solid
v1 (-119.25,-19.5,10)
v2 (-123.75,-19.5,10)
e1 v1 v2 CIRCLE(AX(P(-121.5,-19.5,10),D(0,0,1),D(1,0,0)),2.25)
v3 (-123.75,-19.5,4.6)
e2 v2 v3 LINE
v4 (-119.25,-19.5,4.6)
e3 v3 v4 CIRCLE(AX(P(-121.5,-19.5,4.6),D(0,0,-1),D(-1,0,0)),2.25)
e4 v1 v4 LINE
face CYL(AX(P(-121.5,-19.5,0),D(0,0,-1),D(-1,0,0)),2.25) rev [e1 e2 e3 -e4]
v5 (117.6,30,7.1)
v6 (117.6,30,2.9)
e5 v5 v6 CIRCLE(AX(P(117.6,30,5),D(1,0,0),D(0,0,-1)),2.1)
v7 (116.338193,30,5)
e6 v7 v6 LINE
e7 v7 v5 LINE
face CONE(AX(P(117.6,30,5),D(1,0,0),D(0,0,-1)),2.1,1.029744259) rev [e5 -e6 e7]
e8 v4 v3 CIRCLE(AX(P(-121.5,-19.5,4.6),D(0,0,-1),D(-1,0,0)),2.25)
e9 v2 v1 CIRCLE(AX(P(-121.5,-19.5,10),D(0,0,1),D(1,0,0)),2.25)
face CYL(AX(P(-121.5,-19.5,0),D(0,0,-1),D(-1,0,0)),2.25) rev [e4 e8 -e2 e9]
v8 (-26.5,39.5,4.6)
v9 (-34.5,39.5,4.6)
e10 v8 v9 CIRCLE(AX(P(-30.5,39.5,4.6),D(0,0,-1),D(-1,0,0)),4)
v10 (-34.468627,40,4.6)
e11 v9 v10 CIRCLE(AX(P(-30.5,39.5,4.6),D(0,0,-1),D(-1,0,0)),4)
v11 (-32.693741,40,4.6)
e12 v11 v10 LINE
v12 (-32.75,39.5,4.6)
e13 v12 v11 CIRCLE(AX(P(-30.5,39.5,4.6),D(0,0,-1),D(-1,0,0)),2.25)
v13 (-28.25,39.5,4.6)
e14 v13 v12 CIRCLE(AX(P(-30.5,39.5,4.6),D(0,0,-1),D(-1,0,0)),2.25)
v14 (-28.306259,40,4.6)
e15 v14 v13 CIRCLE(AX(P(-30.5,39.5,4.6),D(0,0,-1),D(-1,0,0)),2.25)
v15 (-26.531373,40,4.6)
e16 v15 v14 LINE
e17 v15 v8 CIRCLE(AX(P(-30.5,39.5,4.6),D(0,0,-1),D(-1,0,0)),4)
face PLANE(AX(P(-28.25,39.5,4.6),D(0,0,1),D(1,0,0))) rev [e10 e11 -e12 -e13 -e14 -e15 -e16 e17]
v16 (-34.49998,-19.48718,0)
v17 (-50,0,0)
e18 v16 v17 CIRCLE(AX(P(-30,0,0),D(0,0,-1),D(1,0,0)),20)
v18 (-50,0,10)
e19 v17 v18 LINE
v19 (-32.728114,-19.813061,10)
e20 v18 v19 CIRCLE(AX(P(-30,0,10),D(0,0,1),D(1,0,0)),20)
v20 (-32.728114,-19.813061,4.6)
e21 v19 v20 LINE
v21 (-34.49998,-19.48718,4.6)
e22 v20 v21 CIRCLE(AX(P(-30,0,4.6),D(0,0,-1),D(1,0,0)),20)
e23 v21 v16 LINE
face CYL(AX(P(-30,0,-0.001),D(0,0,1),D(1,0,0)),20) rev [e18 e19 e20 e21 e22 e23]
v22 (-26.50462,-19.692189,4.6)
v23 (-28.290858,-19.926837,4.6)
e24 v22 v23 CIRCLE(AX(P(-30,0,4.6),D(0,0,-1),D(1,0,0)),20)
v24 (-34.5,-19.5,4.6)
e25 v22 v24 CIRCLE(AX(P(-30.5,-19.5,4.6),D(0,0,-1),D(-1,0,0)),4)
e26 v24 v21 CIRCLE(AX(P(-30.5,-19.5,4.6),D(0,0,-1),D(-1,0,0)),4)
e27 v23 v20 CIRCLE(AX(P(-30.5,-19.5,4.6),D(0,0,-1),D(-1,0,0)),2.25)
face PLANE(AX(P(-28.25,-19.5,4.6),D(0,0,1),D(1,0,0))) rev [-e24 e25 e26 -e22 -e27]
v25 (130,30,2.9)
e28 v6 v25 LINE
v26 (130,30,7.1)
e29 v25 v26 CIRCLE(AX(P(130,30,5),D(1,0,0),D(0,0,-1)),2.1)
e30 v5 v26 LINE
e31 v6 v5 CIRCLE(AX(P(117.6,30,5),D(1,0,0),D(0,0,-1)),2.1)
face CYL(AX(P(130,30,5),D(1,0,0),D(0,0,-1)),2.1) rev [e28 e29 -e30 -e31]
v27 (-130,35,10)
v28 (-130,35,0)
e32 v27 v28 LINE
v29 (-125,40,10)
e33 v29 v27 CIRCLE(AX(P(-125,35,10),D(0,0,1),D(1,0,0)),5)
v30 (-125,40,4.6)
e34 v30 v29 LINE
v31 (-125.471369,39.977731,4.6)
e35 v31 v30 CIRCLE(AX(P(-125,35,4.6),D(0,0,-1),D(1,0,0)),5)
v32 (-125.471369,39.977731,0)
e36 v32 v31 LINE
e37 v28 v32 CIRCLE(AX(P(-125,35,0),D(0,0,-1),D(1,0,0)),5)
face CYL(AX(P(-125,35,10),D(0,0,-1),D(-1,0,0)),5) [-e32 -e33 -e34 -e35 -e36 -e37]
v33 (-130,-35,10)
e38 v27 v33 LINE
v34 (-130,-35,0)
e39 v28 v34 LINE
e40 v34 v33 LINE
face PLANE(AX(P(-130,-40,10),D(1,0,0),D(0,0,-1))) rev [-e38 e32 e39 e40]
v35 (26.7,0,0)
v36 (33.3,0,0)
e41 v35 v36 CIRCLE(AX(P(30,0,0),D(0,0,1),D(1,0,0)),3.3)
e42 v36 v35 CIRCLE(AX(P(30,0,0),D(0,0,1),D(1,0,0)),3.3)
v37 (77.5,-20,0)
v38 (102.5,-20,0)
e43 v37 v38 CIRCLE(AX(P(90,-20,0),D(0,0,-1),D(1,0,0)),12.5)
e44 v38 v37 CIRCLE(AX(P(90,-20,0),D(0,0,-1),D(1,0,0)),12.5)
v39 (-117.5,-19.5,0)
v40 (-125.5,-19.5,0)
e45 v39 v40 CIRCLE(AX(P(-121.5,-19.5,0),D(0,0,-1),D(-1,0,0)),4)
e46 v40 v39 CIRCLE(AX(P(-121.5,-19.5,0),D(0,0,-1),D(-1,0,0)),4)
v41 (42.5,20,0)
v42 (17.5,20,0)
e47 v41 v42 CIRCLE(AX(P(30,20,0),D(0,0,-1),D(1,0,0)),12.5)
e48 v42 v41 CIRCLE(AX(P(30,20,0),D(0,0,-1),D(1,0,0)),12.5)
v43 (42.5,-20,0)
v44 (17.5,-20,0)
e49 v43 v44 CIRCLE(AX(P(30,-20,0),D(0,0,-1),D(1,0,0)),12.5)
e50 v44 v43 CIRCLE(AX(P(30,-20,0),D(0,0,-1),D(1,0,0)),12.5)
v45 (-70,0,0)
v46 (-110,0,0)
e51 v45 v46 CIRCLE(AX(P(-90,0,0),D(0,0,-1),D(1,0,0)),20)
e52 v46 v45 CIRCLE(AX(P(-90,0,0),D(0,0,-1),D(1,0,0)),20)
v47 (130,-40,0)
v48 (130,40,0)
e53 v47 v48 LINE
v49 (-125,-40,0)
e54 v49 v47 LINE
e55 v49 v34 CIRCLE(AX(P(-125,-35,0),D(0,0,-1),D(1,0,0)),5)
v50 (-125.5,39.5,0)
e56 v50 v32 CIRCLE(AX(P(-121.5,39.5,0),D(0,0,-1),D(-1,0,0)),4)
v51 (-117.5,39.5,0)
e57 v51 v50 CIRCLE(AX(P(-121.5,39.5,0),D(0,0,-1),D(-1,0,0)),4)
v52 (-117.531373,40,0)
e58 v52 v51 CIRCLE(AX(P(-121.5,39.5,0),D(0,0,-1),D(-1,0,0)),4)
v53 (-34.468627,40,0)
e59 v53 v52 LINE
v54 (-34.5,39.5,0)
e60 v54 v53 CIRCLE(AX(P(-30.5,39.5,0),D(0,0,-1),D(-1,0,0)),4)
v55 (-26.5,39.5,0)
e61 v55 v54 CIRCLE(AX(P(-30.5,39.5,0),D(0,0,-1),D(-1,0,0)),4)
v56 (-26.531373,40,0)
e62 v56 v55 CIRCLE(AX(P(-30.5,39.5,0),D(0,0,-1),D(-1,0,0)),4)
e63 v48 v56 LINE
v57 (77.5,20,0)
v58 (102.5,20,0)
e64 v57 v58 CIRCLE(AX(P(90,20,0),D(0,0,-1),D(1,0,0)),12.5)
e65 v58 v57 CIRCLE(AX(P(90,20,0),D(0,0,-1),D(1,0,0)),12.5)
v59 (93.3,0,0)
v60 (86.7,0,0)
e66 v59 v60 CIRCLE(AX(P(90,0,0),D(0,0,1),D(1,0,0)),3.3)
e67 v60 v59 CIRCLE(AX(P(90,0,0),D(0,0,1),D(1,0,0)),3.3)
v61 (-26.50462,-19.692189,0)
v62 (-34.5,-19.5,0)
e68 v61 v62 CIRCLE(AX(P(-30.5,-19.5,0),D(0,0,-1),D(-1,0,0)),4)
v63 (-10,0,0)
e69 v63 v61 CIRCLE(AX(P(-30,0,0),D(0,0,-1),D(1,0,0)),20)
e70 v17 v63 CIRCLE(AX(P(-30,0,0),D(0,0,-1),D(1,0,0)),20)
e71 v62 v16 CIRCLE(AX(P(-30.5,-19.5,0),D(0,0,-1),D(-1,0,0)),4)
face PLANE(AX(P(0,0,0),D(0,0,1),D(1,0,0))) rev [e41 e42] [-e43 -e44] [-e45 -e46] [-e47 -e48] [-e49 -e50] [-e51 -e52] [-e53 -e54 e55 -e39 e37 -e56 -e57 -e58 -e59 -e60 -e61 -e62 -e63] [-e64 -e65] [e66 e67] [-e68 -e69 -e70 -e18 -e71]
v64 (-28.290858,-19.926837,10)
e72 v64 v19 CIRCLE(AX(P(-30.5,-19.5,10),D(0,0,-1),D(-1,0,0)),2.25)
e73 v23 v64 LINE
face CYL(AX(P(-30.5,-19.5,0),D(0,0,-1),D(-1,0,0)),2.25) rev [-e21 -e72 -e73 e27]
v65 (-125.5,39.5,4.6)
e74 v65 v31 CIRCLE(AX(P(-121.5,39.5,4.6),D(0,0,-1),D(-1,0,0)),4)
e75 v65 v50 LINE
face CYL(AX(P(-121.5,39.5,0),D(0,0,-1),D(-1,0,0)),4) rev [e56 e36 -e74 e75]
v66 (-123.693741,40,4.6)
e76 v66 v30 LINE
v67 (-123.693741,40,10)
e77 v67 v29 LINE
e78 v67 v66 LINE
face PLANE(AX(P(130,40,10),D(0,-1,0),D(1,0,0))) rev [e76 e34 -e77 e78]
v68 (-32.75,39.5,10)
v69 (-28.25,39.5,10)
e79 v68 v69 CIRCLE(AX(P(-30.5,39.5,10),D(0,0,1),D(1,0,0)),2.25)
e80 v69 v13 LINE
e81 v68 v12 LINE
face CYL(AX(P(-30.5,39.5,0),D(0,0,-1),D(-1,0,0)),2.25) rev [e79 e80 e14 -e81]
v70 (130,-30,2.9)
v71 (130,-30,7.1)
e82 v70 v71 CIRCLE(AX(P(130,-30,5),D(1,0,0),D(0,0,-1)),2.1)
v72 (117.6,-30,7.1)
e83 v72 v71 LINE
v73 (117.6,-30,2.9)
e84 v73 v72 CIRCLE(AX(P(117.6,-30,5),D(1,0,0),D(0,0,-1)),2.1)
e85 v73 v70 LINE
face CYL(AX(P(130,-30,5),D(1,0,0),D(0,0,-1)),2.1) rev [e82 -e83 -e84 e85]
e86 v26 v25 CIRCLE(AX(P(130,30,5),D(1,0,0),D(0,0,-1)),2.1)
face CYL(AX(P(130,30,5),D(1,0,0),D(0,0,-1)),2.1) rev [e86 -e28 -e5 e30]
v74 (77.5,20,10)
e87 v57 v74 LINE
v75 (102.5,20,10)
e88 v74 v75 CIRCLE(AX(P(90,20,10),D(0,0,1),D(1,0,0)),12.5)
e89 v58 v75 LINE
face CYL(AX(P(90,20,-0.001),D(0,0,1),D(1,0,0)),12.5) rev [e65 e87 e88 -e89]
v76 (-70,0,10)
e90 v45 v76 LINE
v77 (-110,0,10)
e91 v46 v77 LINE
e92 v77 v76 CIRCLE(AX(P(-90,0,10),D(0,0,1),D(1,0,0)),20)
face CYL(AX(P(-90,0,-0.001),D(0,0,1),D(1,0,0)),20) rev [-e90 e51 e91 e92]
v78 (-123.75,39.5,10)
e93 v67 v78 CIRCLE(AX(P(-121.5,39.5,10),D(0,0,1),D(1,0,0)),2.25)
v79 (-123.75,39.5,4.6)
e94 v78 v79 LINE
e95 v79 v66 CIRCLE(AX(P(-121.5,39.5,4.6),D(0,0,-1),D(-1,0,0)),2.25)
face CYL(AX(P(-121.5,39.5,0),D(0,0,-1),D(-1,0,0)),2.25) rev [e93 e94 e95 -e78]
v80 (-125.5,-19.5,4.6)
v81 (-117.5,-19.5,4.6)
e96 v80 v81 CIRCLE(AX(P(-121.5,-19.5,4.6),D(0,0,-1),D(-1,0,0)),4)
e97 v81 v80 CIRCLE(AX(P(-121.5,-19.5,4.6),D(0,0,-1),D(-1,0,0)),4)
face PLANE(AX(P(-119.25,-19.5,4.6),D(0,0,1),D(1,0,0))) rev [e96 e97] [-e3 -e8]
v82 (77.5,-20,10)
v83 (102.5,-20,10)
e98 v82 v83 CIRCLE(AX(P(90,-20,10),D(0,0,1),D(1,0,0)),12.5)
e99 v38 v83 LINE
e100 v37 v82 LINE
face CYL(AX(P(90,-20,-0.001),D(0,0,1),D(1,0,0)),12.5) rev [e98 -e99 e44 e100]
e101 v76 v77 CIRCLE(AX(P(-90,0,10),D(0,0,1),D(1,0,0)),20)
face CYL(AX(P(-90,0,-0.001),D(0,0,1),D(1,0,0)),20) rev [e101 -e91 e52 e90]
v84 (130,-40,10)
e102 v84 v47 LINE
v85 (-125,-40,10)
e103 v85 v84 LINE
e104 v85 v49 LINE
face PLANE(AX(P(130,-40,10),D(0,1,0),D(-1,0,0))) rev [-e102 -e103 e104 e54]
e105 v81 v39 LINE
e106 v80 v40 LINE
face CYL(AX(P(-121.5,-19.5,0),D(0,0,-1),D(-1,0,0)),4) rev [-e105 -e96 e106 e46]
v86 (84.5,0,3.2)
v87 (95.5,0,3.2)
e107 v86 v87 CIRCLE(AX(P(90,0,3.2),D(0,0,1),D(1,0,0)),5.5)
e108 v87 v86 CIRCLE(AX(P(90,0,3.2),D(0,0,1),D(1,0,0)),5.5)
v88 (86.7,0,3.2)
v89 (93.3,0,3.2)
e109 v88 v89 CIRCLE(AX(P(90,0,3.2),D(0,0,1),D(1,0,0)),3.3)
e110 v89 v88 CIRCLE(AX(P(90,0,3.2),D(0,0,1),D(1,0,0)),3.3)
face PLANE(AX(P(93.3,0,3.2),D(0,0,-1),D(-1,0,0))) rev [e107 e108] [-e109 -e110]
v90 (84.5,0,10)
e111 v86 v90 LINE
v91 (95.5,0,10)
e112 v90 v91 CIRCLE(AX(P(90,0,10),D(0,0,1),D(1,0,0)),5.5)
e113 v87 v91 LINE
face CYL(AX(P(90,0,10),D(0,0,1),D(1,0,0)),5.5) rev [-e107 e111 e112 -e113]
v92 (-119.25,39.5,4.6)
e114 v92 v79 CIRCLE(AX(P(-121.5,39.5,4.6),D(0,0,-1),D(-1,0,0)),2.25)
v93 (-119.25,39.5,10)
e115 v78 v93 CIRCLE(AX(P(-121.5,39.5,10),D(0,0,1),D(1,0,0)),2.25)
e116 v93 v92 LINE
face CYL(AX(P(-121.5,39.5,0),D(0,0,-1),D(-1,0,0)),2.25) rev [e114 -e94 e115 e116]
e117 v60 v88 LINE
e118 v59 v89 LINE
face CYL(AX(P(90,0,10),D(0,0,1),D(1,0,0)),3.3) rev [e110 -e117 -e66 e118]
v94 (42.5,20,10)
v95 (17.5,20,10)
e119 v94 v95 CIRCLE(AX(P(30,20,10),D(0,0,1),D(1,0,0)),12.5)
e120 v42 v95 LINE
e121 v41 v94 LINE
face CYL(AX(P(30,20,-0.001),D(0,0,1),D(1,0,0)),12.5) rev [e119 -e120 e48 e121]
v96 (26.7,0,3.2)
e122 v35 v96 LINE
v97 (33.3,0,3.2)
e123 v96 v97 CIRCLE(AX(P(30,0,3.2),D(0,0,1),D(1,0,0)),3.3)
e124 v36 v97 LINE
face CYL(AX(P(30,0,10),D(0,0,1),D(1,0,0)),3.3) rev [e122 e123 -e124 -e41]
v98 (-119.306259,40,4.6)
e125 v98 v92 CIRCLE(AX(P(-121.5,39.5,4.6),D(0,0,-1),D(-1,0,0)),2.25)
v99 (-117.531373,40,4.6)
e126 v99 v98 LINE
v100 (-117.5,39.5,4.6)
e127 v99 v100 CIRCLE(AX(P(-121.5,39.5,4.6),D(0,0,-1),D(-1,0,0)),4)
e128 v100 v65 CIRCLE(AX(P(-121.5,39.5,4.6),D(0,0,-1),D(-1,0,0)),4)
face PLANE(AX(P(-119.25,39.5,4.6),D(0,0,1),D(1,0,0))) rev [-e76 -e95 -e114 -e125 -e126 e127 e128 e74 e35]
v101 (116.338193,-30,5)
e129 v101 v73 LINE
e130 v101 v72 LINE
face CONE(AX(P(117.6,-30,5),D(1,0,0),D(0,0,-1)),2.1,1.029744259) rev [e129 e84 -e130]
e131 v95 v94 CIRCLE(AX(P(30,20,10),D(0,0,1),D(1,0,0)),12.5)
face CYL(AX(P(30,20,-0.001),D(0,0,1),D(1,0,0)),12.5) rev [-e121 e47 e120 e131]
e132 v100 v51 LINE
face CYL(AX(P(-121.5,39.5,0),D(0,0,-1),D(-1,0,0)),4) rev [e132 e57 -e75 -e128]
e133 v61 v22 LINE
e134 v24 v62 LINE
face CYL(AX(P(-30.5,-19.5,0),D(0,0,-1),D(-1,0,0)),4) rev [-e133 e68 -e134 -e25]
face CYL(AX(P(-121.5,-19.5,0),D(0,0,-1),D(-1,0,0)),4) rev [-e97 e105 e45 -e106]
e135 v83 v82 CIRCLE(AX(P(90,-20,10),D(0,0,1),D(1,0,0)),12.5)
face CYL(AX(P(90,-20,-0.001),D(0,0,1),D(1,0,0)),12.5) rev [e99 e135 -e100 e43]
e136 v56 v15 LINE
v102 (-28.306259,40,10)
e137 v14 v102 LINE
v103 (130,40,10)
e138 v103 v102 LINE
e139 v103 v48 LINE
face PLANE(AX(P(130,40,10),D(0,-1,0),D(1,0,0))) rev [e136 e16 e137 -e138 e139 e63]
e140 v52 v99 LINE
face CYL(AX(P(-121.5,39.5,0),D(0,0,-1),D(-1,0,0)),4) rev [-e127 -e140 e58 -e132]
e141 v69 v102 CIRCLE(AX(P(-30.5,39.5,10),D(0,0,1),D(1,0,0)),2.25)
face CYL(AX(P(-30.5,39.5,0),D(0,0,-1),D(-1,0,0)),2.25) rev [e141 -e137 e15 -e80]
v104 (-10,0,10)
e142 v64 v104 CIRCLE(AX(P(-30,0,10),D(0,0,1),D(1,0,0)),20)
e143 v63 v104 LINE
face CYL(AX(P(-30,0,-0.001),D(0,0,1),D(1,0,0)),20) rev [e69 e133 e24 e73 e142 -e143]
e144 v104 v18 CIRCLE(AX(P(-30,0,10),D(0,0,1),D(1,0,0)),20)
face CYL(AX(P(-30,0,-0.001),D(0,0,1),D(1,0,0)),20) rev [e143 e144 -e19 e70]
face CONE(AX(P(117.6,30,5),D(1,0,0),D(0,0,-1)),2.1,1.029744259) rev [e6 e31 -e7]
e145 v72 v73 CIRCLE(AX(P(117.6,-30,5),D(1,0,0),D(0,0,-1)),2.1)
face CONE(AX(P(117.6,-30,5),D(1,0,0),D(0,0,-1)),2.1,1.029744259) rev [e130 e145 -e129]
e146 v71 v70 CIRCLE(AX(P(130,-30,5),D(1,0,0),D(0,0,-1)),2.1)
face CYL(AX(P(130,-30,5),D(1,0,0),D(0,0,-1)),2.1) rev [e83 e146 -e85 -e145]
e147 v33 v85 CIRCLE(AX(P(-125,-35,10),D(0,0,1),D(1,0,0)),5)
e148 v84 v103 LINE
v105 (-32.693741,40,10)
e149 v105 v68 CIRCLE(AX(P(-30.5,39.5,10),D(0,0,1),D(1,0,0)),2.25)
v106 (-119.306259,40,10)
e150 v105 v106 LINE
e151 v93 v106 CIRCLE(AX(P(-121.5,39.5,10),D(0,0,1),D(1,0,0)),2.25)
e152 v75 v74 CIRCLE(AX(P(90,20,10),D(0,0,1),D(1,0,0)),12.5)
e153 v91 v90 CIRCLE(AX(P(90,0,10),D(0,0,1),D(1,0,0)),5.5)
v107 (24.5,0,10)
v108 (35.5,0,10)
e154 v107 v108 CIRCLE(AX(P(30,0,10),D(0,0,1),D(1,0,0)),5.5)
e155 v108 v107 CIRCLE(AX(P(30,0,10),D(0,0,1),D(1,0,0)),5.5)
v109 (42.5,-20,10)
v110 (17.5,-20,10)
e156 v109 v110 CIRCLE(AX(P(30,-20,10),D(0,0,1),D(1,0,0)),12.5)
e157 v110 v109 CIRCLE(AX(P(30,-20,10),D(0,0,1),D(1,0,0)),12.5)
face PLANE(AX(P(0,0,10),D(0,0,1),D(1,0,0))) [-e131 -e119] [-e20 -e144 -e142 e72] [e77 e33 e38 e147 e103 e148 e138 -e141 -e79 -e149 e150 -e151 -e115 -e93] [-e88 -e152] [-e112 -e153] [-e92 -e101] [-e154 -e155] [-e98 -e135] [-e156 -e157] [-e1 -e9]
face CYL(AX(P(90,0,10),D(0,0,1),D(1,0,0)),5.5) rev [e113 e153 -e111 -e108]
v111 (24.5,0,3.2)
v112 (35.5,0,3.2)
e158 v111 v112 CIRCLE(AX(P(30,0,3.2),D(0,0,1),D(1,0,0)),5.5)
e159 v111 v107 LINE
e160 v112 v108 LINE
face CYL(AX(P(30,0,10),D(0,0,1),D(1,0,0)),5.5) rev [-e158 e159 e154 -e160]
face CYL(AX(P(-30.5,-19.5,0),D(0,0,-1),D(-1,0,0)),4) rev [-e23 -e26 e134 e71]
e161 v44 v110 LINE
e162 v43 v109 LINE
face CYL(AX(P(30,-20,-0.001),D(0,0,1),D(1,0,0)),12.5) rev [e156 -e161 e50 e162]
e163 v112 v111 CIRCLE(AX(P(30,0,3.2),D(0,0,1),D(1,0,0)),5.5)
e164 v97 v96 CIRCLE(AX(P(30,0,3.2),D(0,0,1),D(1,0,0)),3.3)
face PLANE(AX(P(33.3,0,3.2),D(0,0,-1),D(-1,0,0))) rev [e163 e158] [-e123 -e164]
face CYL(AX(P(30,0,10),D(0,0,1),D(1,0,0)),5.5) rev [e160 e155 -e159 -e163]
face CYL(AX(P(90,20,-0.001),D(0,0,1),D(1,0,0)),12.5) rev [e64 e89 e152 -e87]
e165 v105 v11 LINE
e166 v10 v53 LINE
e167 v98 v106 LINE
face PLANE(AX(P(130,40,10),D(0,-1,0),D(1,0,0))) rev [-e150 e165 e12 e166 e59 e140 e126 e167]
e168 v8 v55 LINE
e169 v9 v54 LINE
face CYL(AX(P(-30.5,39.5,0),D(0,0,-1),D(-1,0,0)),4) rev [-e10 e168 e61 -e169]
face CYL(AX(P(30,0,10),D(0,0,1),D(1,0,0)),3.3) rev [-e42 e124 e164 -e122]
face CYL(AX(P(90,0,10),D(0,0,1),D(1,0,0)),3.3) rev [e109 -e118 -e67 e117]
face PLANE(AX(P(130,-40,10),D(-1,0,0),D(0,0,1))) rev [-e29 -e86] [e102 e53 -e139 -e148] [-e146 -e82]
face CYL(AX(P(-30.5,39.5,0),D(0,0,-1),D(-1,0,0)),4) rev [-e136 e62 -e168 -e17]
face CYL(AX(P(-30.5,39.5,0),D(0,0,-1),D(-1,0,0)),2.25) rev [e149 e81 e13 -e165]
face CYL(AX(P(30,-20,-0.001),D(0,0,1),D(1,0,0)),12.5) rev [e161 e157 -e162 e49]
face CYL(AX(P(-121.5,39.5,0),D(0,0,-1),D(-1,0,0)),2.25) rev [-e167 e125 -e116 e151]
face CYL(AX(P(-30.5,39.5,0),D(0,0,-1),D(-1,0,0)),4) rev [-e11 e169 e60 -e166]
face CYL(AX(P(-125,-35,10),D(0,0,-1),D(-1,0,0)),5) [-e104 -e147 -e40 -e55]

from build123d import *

# Parameters (mm, degrees)
SKETCH_1_W                = 260
SKETCH_1_H                = 80
EXTRUDE_1_DEPTH           = 10
CUT_EXTRUDE_1_REACH       = 138.382
SKETCH_2_R                = 20
CUT_EXTRUDE_2_REACH       = 138.382
SKETCH_3_R                = 12.5
HOLE_WIZARD_M5_1_D        = 4.2
HOLE_WIZARD_M5_1_DEPTH    = 12.4
HOLE_WIZARD_M5_1_TIP      = 1.2618073
HOLE_WIZARD_1_D           = 6.6
HOLE_WIZARD_1_CBORE_D     = 11
HOLE_WIZARD_1_CBORE_DEPTH = 6.8
HOLE_WIZARD_2_D           = 4.5
HOLE_WIZARD_2_DEPTH       = 10
HOLE_WIZARD_2_CBORE_D     = 8
HOLE_WIZARD_2_CBORE_DEPTH = 4.6
FILLET_1_R                = 5


with BuildPart() as part:
    # 草图1 → 凸台-拉伸1 (new body)
    with BuildSketch(Plane.XY):
        Rectangle(SKETCH_1_W, SKETCH_1_H)
    extrude(amount=EXTRUDE_1_DEPTH)

    # 草图2 → 切除-拉伸1 (cut, up to next)
    with BuildSketch(Plane.XY.offset(10), mode=Mode.PRIVATE) as cut_extrude_1_sk1:
        with Locations((-90, 0)):
            Circle(SKETCH_2_R)
    cut_extrude_1_tool1 = extrude(cut_extrude_1_sk1.sketch, amount=-CUT_EXTRUDE_1_REACH, mode=Mode.PRIVATE) & part.part
    # 草图2 → 切除-拉伸1 (cut, up to next)
    with BuildSketch(Plane.XY.offset(10), mode=Mode.PRIVATE) as cut_extrude_1_sk2:
        with Locations((-30, 0)):
            Circle(SKETCH_2_R)
    cut_extrude_1_tool2 = extrude(cut_extrude_1_sk2.sketch, amount=-CUT_EXTRUDE_1_REACH, mode=Mode.PRIVATE) & part.part
    add(cut_extrude_1_tool1.solids().sort_by_distance((-90, 0, 10))[0], mode=Mode.SUBTRACT)
    add(cut_extrude_1_tool2.solids().sort_by_distance((-30, 0, 10))[0], mode=Mode.SUBTRACT)

    # 草图3 → 切除-拉伸2 (cut, up to next)
    with BuildSketch(Plane.XY.offset(10), mode=Mode.PRIVATE) as cut_extrude_2_sk1:
        with Locations((30, -20)):
            Circle(SKETCH_3_R)
    cut_extrude_2_tool1 = extrude(cut_extrude_2_sk1.sketch, amount=-CUT_EXTRUDE_2_REACH, mode=Mode.PRIVATE) & part.part
    # 草图3 → 切除-拉伸2 (cut, up to next)
    with BuildSketch(Plane.XY.offset(10), mode=Mode.PRIVATE) as cut_extrude_2_sk2:
        with Locations((90, -20)):
            Circle(SKETCH_3_R)
    cut_extrude_2_tool2 = extrude(cut_extrude_2_sk2.sketch, amount=-CUT_EXTRUDE_2_REACH, mode=Mode.PRIVATE) & part.part
    # 草图3 → 切除-拉伸2 (cut, up to next)
    with BuildSketch(Plane.XY.offset(10), mode=Mode.PRIVATE) as cut_extrude_2_sk3:
        with Locations((30, 20)):
            Circle(SKETCH_3_R)
    cut_extrude_2_tool3 = extrude(cut_extrude_2_sk3.sketch, amount=-CUT_EXTRUDE_2_REACH, mode=Mode.PRIVATE) & part.part
    # 草图3 → 切除-拉伸2 (cut, up to next)
    with BuildSketch(Plane.XY.offset(10), mode=Mode.PRIVATE) as cut_extrude_2_sk4:
        with Locations((90, 20)):
            Circle(SKETCH_3_R)
    cut_extrude_2_tool4 = extrude(cut_extrude_2_sk4.sketch, amount=-CUT_EXTRUDE_2_REACH, mode=Mode.PRIVATE) & part.part
    add(cut_extrude_2_tool1.solids().sort_by_distance((30, -20, 10))[0], mode=Mode.SUBTRACT)
    add(cut_extrude_2_tool2.solids().sort_by_distance((90, -20, 10))[0], mode=Mode.SUBTRACT)
    add(cut_extrude_2_tool3.solids().sort_by_distance((30, 20, 10))[0], mode=Mode.SUBTRACT)
    add(cut_extrude_2_tool4.solids().sort_by_distance((90, 20, 10))[0], mode=Mode.SUBTRACT)

    # M5 螺纹孔1
    with Locations(Plane(origin=(130, 0, 0), x_dir=(0, 0, -1), z_dir=(1, 0, 0))):
        with Locations((-5, 30), (-5, -30)):
            Hole(HOLE_WIZARD_M5_1_D / 2, depth=HOLE_WIZARD_M5_1_DEPTH)
            with Locations((0, 0, -(HOLE_WIZARD_M5_1_DEPTH + HOLE_WIZARD_M5_1_TIP / 2))):  # 118° drill point
                Cone(0, HOLE_WIZARD_M5_1_D / 2, HOLE_WIZARD_M5_1_TIP, mode=Mode.SUBTRACT)

    # 打孔尺寸(%根据)内六角圆柱头螺钉的类型1 (through all)
    with Locations(Plane.XY.offset(10)):
        with Locations((90, 0), (30, 0)):
            CounterBoreHole(HOLE_WIZARD_1_D / 2, HOLE_WIZARD_1_CBORE_D / 2, HOLE_WIZARD_1_CBORE_DEPTH)

    # 打孔尺寸(%根据)内六角圆柱头螺钉的类型2
    with Locations(Plane(origin=(0, 0, 0), x_dir=(-1, 0, 0), z_dir=(0, 0, -1))):
        with Locations((30.500000316, -19.5), (30.500000316, 39.5), (121.500000316, 39.5), (121.500000316, -19.5)):
            CounterBoreHole(HOLE_WIZARD_2_D / 2, HOLE_WIZARD_2_CBORE_D / 2, HOLE_WIZARD_2_CBORE_DEPTH, depth=HOLE_WIZARD_2_DEPTH)

    # 圆角1
    fillet_1_edges = [part.edges().sort_by_distance(p)[0] for p in [
        (-130, 40, 5),
        (-130, -40, 5),
    ]]
    fillet(fillet_1_edges, radius=FILLET_1_R)


solid = part.part
